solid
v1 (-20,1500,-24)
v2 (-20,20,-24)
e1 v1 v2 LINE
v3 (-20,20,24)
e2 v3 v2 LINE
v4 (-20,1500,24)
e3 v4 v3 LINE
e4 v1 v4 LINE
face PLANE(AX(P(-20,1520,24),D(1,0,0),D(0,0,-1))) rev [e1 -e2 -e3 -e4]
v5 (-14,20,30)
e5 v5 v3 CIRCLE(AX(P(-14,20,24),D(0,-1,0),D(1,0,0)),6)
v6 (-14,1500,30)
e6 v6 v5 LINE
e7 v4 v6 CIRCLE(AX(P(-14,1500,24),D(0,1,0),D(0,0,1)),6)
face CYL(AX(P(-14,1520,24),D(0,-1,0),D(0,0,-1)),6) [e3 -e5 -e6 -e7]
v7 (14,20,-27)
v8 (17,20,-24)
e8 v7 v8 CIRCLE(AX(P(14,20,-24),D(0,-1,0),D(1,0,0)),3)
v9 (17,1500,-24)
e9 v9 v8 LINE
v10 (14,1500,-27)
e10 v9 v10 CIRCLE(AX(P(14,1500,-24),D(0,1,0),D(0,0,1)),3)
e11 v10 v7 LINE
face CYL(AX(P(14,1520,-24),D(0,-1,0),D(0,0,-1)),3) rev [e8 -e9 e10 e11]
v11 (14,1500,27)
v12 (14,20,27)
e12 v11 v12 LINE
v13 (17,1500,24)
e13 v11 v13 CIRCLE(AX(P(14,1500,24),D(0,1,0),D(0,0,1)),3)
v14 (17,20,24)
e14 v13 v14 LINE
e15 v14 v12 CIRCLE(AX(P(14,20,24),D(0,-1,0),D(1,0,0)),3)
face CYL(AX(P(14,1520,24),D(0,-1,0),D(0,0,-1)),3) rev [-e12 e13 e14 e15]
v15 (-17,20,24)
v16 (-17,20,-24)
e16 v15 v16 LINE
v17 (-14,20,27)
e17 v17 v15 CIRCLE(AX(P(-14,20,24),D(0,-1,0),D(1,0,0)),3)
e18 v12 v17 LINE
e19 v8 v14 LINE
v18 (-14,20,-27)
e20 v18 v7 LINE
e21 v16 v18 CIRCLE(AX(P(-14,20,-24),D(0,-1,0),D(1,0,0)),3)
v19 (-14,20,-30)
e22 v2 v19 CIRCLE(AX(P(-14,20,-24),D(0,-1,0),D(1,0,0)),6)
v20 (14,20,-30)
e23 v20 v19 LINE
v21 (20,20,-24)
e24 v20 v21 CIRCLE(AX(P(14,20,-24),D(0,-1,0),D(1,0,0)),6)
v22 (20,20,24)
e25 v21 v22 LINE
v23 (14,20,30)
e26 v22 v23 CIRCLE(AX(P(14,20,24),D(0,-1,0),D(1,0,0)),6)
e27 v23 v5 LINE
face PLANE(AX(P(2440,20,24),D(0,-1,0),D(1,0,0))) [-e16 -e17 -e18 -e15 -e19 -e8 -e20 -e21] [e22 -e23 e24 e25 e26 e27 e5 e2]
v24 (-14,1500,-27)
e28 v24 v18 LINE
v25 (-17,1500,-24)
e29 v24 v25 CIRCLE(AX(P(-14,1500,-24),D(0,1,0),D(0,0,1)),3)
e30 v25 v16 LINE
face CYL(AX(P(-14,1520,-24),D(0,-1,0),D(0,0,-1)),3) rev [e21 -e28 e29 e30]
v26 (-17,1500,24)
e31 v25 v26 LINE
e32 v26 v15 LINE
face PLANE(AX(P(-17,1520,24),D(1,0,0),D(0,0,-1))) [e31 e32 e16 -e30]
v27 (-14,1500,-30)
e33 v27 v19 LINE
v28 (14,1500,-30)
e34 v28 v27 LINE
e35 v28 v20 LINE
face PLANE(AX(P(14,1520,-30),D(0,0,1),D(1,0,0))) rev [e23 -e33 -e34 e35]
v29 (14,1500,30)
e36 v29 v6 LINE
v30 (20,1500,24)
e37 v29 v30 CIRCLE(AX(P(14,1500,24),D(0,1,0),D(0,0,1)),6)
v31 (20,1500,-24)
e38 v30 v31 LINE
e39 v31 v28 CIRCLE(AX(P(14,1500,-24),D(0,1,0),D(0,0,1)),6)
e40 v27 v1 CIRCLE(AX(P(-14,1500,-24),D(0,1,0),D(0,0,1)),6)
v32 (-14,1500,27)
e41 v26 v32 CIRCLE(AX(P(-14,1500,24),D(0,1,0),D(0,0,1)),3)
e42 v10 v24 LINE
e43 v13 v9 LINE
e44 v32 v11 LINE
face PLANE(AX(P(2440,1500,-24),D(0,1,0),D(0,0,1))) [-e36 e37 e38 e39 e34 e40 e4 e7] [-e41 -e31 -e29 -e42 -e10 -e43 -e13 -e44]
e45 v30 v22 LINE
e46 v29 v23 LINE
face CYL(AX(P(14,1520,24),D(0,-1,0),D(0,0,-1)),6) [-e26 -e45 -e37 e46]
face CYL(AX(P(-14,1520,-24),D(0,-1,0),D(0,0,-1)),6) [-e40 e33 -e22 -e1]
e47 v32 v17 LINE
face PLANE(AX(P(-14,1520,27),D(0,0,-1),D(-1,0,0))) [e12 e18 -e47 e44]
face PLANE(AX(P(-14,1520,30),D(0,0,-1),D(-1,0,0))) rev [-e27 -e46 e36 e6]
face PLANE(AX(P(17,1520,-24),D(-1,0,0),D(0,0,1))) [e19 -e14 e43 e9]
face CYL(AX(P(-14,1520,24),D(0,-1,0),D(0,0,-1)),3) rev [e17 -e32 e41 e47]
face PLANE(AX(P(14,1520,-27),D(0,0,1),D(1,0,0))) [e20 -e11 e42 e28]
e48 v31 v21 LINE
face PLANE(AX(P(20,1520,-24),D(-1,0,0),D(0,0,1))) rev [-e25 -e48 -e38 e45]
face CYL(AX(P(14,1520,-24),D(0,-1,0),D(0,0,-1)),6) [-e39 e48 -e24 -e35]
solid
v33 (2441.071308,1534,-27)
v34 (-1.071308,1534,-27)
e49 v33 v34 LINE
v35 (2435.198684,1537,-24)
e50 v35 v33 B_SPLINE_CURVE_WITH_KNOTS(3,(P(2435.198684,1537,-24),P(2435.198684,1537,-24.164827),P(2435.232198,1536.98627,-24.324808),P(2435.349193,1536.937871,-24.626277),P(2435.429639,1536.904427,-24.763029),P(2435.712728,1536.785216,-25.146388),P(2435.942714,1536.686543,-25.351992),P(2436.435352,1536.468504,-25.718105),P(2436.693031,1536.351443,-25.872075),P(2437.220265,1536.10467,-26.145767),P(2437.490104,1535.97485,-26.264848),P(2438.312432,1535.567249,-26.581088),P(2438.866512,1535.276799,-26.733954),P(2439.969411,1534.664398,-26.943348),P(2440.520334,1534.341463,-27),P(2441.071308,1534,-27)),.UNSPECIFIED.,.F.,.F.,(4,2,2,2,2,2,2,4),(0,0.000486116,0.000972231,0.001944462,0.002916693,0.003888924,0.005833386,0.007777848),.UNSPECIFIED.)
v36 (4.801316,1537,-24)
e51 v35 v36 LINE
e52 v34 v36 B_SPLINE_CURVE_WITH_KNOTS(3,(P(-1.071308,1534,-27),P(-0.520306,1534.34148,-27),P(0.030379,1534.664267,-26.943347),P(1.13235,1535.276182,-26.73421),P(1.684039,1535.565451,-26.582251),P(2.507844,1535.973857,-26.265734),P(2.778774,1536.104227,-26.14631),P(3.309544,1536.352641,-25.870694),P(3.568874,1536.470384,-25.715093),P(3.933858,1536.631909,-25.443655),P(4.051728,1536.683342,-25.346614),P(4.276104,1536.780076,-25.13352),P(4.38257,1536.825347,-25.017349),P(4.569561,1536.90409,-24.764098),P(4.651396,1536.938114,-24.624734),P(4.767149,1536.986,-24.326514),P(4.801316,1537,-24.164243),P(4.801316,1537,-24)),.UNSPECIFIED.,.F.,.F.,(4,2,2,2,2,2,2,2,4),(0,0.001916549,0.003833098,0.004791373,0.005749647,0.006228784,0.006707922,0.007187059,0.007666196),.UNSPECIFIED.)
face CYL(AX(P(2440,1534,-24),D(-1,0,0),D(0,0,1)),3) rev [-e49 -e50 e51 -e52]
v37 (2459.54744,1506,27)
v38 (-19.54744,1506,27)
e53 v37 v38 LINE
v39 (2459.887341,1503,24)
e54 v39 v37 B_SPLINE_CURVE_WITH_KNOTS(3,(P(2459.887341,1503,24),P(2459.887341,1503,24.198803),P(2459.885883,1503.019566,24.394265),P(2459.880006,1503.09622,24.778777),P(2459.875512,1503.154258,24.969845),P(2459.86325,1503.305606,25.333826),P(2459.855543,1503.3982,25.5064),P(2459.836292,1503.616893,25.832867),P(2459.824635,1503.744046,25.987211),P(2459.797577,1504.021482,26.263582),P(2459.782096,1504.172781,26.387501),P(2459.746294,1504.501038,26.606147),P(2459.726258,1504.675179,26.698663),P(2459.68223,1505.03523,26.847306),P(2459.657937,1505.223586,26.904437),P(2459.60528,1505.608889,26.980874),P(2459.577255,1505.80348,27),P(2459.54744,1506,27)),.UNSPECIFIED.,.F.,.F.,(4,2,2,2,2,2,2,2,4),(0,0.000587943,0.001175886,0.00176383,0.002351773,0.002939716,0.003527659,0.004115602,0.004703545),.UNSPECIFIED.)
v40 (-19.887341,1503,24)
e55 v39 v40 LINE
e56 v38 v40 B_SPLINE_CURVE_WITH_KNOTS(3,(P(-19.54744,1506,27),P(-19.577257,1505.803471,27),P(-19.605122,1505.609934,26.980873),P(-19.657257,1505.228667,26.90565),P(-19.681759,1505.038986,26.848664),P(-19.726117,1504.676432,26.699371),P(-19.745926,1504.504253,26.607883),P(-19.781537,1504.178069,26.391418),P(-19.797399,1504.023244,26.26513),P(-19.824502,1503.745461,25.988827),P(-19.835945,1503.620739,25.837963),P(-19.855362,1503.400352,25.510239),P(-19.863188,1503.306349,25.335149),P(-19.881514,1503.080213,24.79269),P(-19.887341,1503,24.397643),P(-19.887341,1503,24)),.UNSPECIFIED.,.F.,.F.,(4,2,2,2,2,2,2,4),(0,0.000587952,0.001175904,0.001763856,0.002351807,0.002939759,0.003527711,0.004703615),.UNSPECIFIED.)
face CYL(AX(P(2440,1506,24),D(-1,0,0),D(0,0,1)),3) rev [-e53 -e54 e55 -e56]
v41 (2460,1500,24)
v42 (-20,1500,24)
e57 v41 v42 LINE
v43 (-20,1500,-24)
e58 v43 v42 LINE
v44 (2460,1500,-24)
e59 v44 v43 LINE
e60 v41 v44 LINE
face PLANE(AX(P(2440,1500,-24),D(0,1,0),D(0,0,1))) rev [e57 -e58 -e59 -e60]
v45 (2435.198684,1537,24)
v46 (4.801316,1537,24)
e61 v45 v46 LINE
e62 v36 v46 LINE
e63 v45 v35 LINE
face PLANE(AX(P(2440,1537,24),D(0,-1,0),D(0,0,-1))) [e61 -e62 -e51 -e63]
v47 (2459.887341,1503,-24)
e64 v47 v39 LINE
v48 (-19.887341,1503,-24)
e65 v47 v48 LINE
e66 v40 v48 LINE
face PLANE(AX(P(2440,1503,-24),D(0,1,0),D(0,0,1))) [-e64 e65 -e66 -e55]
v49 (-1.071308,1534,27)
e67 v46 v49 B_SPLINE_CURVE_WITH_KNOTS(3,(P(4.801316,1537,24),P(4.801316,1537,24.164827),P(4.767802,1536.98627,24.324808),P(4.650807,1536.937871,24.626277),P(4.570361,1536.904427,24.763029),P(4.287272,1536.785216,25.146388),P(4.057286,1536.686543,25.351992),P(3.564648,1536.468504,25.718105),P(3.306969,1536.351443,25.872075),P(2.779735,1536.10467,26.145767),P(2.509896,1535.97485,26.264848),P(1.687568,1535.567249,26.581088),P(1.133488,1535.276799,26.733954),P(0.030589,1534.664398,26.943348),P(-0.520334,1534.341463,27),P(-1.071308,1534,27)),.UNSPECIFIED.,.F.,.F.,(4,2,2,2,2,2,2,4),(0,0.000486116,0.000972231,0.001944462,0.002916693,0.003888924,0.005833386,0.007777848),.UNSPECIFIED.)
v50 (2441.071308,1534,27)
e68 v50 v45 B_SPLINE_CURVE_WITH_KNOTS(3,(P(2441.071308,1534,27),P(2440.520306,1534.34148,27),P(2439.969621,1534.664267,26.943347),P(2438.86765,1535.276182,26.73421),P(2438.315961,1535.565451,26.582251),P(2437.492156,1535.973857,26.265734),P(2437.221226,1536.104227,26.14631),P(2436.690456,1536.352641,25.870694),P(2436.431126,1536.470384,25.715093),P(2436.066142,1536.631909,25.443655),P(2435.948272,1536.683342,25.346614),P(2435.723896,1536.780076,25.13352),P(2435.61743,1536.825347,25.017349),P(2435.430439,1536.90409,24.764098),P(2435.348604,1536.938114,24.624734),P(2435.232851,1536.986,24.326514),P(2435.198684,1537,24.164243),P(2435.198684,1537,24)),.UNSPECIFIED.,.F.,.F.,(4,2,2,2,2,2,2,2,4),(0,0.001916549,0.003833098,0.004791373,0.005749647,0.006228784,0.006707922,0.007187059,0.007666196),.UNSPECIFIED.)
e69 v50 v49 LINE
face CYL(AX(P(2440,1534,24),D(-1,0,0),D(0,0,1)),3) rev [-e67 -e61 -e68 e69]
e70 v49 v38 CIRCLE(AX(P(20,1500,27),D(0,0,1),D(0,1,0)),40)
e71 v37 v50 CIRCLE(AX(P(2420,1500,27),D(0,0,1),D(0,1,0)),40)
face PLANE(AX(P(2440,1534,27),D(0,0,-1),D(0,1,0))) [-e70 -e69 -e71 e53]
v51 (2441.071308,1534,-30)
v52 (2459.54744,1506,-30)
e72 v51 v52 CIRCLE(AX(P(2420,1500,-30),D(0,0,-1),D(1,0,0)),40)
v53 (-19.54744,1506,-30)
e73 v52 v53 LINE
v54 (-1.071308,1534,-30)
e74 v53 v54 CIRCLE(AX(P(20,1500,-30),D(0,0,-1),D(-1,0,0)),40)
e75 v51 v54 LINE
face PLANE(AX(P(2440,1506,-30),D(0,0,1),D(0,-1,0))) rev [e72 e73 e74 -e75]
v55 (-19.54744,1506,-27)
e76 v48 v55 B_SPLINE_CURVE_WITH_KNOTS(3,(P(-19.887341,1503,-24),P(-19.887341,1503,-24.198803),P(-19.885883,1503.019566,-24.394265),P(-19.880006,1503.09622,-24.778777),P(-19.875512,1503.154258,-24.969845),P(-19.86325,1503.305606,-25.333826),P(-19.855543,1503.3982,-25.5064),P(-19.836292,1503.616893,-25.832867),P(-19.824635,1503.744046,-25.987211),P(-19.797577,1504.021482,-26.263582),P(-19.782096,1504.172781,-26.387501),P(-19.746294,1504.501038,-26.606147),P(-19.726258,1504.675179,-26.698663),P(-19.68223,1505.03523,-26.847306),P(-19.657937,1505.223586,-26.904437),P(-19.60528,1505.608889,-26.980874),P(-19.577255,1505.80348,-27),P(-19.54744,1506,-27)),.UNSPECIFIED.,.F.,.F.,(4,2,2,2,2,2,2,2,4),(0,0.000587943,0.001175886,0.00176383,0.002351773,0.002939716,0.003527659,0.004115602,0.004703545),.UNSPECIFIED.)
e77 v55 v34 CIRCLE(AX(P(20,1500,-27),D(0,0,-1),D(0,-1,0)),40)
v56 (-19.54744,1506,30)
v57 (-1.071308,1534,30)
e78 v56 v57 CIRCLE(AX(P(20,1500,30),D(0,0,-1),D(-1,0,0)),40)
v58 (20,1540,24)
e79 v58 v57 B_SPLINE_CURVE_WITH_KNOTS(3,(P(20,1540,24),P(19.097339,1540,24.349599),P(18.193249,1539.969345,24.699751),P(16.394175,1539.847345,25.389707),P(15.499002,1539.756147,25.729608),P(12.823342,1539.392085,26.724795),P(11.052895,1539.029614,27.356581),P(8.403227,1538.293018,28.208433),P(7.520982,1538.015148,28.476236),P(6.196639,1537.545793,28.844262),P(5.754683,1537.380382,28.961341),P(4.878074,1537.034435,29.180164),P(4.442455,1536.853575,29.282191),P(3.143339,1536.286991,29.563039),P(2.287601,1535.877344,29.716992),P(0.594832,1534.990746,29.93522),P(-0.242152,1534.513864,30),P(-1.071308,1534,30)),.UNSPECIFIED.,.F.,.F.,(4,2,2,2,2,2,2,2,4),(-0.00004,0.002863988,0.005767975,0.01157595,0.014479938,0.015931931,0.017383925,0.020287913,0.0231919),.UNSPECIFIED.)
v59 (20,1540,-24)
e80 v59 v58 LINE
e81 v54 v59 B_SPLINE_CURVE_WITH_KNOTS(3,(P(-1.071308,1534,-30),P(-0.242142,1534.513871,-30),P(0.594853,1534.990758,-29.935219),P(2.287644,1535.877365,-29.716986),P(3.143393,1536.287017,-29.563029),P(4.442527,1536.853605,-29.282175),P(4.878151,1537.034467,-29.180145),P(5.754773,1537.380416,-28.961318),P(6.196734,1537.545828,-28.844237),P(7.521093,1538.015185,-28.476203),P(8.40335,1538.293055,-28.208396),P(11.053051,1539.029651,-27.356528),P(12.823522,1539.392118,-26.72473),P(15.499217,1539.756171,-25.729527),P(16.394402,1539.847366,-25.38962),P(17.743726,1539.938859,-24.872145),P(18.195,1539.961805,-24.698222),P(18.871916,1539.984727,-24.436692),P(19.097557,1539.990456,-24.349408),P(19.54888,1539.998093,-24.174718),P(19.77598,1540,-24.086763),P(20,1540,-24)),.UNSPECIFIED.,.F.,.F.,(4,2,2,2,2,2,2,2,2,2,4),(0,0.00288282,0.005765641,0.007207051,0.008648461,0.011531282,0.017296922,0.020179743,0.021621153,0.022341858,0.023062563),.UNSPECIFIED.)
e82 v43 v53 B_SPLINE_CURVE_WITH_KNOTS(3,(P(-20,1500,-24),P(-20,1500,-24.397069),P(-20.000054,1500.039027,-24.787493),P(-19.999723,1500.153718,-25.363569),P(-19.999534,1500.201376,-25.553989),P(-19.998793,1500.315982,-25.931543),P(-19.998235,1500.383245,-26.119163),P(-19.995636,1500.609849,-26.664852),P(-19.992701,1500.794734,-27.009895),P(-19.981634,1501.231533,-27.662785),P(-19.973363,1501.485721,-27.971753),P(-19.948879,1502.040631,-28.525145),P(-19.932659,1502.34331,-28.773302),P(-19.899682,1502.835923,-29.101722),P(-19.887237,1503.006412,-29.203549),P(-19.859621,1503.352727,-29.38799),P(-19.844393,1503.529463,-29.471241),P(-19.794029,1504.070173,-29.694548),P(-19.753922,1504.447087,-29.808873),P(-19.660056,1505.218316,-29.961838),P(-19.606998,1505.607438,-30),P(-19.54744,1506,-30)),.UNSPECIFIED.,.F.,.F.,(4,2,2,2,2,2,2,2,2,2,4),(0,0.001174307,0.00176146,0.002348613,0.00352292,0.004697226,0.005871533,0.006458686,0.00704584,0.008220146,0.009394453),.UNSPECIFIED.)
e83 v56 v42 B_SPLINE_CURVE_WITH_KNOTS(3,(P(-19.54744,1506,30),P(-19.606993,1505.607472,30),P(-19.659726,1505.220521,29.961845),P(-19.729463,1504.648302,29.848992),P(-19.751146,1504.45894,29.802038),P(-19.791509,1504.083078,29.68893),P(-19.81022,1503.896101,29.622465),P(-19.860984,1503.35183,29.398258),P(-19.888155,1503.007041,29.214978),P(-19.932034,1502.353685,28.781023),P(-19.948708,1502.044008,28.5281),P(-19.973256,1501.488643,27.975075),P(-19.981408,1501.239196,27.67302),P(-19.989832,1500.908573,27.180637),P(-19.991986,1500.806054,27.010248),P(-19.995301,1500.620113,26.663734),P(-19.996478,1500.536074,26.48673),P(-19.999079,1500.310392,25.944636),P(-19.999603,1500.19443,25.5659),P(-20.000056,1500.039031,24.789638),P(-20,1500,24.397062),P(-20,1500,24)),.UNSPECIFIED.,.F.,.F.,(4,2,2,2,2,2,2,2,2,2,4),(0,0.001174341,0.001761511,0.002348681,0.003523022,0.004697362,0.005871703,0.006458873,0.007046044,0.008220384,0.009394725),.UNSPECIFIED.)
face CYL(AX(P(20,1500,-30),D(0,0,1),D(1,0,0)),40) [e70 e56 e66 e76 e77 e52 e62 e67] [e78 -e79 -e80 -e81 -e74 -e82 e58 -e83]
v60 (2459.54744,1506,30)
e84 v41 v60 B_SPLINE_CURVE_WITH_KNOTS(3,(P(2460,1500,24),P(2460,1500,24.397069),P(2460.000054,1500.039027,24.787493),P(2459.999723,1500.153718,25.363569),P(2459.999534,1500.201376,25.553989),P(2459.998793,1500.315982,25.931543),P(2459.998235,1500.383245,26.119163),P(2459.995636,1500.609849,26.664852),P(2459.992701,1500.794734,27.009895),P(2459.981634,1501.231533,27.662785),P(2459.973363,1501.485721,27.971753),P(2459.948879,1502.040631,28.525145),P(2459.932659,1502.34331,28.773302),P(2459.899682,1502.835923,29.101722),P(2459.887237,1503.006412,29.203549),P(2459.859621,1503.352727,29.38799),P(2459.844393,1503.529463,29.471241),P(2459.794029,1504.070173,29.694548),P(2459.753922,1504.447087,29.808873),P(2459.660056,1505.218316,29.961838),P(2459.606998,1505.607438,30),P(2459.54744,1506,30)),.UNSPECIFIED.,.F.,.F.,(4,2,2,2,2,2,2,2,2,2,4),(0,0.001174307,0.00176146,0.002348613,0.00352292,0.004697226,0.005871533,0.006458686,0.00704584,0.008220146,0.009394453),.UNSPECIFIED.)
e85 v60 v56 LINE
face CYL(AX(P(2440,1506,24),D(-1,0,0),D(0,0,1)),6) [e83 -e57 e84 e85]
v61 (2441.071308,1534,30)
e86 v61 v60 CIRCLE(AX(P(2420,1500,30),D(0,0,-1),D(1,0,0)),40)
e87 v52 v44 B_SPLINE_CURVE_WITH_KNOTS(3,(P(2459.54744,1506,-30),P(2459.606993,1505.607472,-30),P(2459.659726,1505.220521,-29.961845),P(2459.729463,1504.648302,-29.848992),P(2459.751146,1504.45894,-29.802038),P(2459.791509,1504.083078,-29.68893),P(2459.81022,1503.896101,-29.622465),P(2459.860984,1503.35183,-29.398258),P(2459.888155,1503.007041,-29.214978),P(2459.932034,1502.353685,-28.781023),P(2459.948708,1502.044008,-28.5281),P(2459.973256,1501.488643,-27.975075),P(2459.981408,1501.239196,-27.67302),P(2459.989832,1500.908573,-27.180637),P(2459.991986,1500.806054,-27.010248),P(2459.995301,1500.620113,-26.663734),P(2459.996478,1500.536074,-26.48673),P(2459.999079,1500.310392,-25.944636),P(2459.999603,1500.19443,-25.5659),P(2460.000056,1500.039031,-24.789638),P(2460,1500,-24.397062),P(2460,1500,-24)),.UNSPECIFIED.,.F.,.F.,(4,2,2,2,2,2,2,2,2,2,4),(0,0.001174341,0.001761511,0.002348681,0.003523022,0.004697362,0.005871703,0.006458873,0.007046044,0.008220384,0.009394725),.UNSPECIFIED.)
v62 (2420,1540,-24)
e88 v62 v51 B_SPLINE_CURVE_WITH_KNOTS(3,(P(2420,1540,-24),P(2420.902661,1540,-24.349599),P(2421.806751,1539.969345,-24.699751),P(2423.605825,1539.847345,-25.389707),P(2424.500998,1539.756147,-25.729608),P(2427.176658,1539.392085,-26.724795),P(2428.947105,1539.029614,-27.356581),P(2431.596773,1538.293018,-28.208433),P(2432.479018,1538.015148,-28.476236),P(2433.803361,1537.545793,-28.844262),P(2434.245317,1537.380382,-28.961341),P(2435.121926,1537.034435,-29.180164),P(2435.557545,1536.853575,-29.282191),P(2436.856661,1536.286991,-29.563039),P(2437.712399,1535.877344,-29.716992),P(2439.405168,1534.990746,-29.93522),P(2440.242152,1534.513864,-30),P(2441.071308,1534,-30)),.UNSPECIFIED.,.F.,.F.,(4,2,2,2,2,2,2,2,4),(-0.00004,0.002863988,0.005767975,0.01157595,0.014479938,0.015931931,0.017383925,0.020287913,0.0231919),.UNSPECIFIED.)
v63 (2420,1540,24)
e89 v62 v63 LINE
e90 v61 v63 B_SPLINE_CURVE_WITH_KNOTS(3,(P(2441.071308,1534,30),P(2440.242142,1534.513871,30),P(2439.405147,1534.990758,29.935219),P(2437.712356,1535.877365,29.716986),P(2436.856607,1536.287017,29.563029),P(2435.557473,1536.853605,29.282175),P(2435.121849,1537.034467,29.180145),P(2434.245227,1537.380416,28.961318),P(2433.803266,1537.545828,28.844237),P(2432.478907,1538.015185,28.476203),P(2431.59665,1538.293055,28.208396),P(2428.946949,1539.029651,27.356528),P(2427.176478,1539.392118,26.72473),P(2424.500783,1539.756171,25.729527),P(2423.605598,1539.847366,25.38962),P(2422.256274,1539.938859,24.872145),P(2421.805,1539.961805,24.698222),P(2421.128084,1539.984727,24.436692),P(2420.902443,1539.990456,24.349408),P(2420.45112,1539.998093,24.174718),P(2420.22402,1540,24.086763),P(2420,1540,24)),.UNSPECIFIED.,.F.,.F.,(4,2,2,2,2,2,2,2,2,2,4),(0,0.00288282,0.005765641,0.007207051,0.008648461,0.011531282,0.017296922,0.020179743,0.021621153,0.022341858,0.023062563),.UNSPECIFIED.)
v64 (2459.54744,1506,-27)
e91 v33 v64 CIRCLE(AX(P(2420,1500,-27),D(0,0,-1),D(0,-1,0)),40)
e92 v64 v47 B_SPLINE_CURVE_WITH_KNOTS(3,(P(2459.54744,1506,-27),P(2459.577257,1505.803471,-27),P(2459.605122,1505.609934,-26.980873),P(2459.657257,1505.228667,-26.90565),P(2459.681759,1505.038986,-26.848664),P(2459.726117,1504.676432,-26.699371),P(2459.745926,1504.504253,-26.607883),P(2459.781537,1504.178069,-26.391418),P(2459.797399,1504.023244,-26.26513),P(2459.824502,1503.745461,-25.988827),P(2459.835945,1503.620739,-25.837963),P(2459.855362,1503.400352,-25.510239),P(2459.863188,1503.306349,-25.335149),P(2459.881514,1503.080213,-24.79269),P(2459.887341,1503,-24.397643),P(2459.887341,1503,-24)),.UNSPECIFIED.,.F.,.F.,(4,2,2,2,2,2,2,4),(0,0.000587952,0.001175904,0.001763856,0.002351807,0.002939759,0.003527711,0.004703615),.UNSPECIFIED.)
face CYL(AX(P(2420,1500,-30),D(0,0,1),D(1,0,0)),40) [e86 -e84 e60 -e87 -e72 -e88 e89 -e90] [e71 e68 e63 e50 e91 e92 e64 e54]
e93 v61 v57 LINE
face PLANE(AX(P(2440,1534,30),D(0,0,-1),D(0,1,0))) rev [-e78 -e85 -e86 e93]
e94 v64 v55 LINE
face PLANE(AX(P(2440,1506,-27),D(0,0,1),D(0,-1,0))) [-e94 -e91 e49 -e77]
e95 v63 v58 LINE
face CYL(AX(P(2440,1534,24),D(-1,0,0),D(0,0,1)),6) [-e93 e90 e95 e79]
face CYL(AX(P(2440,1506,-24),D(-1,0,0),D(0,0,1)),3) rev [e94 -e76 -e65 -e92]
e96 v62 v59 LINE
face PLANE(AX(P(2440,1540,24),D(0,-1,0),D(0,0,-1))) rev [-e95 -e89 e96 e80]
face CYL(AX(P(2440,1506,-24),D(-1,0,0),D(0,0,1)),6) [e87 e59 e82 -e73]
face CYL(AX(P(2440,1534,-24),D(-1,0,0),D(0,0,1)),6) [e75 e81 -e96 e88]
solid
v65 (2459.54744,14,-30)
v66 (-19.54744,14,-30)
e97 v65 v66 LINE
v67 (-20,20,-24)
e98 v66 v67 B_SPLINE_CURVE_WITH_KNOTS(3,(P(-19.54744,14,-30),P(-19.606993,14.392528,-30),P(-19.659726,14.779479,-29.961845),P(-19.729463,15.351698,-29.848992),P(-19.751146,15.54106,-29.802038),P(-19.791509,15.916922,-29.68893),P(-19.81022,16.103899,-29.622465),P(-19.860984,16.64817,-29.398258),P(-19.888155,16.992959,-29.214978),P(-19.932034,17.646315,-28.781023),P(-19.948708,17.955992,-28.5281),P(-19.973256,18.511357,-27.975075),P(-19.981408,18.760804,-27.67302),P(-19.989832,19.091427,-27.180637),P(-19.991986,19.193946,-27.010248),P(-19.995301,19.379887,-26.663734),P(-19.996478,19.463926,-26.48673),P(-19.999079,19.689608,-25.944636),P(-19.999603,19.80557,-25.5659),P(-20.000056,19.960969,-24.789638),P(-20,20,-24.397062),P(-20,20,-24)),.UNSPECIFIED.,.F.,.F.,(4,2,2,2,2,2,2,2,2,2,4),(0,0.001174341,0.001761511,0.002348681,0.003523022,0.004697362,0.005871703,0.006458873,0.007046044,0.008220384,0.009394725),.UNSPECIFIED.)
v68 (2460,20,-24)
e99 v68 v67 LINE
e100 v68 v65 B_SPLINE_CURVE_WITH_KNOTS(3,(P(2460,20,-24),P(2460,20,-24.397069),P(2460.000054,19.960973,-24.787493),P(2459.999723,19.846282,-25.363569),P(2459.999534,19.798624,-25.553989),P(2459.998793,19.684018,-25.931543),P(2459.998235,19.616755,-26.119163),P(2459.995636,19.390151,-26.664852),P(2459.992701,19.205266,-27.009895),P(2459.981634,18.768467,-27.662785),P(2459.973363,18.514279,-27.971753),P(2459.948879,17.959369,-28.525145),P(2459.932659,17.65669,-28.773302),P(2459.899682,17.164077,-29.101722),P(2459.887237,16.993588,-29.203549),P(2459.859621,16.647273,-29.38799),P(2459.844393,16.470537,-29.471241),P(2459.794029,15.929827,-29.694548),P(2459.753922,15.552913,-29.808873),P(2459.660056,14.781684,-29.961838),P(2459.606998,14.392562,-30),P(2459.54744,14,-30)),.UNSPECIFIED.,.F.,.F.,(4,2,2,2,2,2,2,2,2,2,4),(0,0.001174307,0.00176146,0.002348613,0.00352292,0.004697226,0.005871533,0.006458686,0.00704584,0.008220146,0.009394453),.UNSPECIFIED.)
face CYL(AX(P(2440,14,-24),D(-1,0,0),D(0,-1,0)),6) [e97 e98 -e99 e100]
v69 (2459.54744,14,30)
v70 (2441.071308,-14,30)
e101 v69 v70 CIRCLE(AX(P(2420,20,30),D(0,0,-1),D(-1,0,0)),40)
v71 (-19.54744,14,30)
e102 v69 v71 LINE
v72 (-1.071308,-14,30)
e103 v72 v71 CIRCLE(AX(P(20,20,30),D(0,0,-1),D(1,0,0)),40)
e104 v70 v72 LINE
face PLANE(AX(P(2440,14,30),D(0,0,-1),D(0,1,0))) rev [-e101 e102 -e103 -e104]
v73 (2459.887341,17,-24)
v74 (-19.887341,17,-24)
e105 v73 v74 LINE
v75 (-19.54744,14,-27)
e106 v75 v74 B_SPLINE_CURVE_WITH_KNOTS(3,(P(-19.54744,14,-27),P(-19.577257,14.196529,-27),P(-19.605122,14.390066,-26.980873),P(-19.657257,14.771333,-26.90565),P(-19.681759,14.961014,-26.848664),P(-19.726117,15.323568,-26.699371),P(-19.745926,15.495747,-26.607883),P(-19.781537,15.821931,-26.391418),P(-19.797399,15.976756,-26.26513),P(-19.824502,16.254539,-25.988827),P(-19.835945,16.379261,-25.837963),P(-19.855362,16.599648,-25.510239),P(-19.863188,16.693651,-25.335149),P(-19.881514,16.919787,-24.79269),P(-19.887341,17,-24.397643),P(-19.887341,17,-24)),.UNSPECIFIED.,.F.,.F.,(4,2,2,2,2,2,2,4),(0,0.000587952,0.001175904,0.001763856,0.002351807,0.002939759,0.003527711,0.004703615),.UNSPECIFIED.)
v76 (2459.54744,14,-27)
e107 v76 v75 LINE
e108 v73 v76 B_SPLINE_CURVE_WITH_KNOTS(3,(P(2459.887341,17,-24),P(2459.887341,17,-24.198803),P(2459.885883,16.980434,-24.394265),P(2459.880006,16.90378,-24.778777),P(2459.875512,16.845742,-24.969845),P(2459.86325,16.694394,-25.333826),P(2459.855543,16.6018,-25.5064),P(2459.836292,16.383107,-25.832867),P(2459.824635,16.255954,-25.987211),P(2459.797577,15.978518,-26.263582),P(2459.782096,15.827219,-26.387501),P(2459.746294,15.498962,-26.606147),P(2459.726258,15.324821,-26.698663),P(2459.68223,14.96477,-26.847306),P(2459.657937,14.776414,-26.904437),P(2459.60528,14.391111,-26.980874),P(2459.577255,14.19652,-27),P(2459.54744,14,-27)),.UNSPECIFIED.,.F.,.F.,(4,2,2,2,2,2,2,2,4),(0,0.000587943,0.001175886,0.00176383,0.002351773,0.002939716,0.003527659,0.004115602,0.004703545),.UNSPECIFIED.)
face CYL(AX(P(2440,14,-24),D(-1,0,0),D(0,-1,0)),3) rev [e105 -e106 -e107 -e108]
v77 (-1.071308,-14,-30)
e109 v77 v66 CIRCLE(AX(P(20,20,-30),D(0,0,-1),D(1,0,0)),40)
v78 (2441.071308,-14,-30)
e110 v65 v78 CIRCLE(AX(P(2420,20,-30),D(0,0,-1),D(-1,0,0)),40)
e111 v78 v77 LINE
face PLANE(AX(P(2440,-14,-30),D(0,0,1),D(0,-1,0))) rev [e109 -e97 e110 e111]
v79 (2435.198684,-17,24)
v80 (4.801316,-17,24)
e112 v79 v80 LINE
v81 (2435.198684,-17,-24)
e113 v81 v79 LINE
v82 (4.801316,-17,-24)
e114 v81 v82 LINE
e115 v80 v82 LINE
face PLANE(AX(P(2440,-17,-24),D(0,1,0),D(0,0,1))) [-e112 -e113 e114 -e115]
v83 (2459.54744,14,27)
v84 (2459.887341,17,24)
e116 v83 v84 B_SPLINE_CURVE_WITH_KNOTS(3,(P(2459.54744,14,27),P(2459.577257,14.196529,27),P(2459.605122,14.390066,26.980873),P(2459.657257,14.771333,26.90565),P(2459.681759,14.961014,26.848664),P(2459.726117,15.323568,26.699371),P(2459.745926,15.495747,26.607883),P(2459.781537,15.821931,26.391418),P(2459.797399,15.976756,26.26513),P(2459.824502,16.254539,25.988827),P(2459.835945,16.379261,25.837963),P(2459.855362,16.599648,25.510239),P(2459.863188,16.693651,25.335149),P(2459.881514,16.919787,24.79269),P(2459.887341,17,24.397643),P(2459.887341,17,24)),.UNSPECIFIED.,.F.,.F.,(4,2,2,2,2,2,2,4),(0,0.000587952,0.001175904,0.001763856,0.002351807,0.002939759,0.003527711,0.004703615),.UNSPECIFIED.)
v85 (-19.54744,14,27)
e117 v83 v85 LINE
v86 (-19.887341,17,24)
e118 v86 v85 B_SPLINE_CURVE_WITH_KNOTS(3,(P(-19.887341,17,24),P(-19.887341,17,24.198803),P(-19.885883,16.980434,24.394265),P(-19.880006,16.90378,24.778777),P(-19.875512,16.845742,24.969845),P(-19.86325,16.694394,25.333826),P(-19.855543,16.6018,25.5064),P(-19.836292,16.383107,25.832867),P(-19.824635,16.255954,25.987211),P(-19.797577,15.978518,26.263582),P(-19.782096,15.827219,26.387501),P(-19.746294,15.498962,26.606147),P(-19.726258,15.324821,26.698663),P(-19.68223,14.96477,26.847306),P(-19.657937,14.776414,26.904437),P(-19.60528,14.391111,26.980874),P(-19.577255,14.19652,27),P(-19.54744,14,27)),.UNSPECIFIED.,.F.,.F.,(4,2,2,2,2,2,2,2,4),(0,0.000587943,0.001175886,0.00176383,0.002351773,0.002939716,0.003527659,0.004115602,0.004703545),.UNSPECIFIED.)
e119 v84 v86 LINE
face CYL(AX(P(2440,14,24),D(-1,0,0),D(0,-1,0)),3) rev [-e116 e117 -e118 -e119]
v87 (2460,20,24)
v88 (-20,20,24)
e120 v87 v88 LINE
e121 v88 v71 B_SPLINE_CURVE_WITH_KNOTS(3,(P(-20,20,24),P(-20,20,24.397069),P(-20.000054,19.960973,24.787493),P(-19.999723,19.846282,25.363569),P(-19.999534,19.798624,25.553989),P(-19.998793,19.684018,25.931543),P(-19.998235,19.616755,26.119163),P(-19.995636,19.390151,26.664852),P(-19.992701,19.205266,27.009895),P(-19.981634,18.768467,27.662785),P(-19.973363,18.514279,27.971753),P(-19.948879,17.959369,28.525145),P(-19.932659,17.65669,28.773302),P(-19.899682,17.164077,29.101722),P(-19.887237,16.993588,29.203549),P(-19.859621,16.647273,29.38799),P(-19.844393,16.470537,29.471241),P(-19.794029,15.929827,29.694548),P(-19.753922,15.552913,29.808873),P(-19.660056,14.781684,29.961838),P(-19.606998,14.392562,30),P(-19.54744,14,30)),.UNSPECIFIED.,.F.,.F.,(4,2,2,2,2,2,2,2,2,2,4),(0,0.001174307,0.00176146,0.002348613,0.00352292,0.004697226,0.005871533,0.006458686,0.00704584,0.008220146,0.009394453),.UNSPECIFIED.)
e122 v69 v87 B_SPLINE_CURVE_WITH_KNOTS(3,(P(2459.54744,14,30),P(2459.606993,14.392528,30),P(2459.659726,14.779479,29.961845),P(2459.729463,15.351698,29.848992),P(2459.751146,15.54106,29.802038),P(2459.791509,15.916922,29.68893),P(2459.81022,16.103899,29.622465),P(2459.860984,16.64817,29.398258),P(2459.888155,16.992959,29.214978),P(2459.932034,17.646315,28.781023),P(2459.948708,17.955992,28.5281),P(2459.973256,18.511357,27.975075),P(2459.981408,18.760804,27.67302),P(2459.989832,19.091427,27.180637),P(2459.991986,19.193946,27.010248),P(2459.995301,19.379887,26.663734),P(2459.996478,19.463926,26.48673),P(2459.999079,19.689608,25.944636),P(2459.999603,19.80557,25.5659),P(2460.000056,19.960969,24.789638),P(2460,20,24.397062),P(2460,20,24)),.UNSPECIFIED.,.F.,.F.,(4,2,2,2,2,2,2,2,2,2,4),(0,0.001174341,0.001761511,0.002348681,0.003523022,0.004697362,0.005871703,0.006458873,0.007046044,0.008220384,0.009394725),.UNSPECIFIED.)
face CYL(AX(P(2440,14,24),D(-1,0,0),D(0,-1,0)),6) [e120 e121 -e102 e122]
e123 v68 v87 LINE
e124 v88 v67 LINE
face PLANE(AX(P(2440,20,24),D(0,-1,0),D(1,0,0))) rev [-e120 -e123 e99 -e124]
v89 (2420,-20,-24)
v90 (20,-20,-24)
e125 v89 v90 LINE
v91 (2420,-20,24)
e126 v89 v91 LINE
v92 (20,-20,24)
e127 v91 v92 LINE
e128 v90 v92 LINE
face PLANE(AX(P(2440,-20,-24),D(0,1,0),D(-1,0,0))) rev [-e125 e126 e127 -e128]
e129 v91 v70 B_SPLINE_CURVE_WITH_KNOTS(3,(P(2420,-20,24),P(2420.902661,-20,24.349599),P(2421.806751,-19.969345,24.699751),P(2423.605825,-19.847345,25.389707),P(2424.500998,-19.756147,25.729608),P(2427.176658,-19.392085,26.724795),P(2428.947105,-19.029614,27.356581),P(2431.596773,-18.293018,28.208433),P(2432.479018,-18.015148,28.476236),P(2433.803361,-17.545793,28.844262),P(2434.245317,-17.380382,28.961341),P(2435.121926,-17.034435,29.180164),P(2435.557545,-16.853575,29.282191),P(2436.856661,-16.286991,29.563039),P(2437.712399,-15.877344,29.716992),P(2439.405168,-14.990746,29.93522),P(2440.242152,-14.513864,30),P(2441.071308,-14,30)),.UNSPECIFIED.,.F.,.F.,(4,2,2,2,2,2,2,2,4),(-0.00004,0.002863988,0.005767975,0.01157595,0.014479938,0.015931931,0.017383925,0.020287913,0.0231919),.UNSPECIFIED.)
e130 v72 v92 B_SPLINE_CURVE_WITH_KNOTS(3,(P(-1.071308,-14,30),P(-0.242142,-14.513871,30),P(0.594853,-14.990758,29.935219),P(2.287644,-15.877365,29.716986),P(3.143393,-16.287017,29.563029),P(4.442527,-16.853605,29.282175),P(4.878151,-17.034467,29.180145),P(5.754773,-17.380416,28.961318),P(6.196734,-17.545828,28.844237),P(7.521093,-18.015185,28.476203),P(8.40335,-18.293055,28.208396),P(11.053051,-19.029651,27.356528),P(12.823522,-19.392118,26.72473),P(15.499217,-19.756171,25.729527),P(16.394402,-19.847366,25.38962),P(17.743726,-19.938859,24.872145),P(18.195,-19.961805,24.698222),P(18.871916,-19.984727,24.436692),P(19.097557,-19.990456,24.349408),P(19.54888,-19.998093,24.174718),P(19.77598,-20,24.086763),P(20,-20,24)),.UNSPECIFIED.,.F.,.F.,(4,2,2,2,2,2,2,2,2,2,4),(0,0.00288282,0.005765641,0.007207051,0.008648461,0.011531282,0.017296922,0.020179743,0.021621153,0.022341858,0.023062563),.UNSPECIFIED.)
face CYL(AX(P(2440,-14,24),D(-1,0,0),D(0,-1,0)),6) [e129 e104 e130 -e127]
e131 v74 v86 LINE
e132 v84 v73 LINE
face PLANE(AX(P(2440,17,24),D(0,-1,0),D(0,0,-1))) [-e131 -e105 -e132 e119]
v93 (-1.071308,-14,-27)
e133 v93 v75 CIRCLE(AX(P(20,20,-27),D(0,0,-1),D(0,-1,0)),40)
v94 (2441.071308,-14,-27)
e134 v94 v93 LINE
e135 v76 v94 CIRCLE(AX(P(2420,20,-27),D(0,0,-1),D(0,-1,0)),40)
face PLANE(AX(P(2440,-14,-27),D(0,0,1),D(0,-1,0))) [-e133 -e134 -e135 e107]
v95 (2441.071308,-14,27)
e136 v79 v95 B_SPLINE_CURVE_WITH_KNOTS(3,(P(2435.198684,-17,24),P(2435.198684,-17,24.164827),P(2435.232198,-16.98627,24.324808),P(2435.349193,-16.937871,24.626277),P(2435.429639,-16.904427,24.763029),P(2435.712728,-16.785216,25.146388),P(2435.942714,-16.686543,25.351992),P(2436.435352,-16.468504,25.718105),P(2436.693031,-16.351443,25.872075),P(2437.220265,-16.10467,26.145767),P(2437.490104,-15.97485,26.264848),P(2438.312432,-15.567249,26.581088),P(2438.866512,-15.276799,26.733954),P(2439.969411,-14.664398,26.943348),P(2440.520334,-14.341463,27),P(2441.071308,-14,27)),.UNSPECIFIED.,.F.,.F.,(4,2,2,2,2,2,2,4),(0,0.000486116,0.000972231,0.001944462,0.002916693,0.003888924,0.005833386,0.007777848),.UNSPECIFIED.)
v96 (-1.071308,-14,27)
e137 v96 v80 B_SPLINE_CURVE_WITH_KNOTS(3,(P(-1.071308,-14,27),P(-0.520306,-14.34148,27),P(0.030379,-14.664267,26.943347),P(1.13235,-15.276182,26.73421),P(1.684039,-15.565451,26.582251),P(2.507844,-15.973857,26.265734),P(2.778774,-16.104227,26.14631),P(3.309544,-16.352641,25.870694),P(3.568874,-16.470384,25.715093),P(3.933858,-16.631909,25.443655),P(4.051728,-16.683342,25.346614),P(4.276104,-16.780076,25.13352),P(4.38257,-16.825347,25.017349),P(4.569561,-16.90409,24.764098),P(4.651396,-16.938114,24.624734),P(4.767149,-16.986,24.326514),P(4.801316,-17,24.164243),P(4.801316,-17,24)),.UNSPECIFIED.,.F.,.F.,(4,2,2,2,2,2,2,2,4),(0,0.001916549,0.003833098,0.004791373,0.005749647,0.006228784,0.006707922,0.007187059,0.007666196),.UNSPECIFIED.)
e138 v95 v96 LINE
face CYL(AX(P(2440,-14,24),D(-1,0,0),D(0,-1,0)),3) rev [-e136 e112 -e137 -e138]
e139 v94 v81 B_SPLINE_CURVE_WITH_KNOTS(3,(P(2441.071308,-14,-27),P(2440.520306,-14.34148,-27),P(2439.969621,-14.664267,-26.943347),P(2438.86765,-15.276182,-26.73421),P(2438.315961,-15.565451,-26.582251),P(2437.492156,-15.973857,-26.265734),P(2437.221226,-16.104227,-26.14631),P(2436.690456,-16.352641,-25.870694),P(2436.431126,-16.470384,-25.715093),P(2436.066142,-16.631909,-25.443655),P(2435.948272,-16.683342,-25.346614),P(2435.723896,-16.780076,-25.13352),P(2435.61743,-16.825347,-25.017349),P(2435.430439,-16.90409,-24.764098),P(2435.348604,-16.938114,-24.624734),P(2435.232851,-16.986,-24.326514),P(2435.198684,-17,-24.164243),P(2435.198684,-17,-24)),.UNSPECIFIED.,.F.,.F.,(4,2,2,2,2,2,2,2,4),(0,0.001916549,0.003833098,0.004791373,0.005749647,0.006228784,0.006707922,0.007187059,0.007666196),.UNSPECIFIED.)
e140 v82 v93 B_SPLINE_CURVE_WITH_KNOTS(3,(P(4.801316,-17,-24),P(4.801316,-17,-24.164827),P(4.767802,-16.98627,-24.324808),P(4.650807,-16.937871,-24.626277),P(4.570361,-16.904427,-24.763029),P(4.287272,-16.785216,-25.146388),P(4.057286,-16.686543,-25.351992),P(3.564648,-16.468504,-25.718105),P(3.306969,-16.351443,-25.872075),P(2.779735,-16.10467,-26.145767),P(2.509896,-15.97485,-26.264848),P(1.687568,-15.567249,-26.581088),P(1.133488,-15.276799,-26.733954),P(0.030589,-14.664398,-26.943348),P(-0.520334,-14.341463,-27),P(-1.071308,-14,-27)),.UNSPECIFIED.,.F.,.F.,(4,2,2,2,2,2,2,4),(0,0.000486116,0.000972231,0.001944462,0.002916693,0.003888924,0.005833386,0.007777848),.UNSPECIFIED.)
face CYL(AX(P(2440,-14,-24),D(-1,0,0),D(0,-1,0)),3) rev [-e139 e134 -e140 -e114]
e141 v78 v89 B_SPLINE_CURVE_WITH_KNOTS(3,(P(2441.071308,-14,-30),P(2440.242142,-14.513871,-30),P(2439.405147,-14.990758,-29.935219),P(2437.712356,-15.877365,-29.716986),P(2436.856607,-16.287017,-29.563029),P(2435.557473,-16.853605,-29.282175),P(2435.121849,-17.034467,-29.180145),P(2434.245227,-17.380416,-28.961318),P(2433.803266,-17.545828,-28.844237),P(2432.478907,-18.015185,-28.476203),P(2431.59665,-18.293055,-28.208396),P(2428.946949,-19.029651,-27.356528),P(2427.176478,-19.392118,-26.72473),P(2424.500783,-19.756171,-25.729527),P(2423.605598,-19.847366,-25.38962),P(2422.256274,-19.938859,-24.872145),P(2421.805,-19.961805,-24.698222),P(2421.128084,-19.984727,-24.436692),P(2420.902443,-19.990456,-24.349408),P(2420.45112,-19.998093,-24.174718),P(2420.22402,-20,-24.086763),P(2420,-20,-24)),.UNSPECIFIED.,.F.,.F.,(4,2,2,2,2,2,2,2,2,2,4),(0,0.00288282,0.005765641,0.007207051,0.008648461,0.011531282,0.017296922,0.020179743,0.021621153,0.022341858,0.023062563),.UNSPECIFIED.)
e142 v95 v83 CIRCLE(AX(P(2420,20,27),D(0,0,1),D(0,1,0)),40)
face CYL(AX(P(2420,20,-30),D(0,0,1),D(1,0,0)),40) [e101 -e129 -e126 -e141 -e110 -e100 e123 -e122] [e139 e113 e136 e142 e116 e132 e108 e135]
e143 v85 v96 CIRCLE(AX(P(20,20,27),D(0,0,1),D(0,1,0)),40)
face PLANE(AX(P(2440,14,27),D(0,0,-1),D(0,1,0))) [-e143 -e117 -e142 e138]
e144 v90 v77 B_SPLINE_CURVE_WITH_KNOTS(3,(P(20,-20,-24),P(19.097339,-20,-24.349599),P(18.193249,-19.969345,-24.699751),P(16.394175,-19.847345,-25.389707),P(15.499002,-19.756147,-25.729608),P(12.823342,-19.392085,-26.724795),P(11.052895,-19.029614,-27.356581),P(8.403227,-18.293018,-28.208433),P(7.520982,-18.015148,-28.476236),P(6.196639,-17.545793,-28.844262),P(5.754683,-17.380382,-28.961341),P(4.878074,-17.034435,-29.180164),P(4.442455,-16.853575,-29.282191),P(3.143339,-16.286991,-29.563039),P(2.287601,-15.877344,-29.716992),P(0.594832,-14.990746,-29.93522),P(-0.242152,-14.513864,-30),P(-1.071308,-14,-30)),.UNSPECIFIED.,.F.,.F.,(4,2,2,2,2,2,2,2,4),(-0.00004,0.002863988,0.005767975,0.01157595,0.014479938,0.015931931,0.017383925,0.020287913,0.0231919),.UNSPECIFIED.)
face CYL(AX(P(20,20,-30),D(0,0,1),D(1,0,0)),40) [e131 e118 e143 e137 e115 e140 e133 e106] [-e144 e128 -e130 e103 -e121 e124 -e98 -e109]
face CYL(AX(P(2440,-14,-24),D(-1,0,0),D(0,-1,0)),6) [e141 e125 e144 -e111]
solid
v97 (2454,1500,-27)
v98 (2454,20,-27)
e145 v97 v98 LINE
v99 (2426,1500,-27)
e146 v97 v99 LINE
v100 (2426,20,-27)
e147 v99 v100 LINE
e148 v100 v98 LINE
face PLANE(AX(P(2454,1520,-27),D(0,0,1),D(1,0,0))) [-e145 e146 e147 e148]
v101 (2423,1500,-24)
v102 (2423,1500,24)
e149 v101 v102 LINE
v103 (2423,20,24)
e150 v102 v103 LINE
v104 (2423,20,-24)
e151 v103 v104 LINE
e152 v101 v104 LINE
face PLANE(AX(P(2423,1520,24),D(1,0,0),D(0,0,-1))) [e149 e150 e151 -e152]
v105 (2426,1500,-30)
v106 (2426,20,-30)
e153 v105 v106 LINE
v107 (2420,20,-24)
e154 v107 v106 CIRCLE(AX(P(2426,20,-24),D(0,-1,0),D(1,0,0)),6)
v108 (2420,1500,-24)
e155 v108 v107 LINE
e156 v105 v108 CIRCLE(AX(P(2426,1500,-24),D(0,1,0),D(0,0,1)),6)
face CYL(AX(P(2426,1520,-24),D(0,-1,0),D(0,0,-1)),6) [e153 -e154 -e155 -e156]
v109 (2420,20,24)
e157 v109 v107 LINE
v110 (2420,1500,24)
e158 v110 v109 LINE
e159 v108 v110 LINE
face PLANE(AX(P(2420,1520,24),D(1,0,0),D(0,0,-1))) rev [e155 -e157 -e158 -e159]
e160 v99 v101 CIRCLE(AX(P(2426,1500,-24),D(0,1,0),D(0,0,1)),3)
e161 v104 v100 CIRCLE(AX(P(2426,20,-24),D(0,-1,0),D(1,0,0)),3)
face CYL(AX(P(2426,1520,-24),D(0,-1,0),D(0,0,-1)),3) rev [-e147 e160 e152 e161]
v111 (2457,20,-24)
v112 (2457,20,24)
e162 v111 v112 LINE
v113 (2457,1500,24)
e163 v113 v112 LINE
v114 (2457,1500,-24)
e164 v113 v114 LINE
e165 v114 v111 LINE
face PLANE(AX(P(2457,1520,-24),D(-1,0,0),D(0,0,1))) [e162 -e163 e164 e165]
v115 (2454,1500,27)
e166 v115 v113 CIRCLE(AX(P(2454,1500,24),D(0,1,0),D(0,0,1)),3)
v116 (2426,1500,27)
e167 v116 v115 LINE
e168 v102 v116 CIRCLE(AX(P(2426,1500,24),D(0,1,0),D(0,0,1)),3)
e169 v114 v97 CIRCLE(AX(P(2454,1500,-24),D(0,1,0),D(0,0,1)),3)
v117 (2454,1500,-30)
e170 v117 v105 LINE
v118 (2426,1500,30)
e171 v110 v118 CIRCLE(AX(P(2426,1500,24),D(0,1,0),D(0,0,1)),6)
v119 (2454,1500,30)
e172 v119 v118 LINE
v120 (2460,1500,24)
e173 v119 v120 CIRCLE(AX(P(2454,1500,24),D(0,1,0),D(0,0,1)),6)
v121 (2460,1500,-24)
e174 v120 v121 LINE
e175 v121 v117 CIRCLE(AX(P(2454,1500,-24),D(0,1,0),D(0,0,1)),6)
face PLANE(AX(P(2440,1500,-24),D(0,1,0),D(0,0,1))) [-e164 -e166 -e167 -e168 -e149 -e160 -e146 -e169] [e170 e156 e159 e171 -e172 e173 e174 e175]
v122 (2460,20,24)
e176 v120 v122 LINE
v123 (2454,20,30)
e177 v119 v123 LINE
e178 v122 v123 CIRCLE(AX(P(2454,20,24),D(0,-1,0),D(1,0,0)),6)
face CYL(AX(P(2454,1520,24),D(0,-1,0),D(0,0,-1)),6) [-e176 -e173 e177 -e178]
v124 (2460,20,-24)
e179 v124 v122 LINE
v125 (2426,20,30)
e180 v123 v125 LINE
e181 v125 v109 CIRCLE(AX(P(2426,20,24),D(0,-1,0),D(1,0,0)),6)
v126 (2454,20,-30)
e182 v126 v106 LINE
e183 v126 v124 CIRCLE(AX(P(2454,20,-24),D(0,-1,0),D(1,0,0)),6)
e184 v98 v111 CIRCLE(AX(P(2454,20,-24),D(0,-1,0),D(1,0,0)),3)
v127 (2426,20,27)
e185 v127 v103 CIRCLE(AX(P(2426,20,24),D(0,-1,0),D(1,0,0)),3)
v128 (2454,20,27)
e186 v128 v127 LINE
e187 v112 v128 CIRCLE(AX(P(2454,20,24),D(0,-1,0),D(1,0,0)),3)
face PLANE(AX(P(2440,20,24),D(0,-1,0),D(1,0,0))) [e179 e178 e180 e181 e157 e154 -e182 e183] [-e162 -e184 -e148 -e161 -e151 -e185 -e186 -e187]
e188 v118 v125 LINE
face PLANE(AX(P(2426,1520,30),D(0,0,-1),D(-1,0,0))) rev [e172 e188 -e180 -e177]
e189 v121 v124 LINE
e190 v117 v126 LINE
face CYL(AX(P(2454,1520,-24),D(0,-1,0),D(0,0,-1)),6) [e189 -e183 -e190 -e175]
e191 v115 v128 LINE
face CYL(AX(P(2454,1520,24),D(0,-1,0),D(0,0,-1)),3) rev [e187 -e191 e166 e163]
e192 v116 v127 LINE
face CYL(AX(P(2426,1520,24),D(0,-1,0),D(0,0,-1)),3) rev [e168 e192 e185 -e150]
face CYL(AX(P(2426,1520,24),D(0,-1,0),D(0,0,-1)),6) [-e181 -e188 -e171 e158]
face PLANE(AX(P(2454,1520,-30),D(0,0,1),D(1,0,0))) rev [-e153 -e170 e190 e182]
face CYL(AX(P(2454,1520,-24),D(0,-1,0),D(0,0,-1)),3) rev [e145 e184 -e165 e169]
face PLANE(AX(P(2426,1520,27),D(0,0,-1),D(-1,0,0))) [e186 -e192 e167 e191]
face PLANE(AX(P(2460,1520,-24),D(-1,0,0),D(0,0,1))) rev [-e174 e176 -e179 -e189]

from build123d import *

# Parameters (mm, degrees)
GB_6728_1986_RECT_HOLLOW_SECTION_060_X_4_DEPTH      = 2460
GB_6728_1986_RECT_HOLLOW_SECTION_060_X_4_DEPTH_BACK = 20
GB_6728_1986_RECT_HOLLOW_SECTION_060_2_DEPTH        = 2480
GB_6728_1986_RECT_HOLLOW_SECTION_060_3_DEPTH        = 1522
GB_6728_1986_RECT_HOLLOW_SECTION_060_5_DEPTH        = 1522
CUT_EXTRUDE1_DEPTH                                  = 2877.6821166058676


with BuildPart() as part:
    # Sketch14 → GB/6728-1986 rect hollow section 060 X 40 X 3(1) (new, two sides: drawn at the far end of the back side and taken through both)
    with BuildSketch(Plane(origin=(0, 1520, 0), x_dir=(0, 1, 3.49e-15), z_dir=(1, 0, 0)).offset(-GB_6728_1986_RECT_HOLLOW_SECTION_060_X_4_DEPTH_BACK)):
        with BuildLine():
            Line((-14, -30), (14, -30))
            ThreePointArc((14, -30), (18.242640687119284, -28.242640687119284), (20.000000000000004, -24))
            Line((20.000000000000004, -24), (20.000000000000004, 24))
            ThreePointArc((20.000000000000004, 24), (18.242640687119287, 28.242640687119287), (14, 30))
            Line((14, 30), (-14, 30))
            ThreePointArc((-14, 30), (-18.242640687119284, 28.242640687119284), (-20.000000000000004, 24))
            Line((-20.000000000000004, 24), (-20.000000000000004, -24))
            ThreePointArc((-20.000000000000004, -24), (-18.242640687119287, -28.242640687119287), (-14, -30))
        make_face()
        with BuildLine():
            Line((-14, -27.000000000000004), (14, -27.000000000000004))
            ThreePointArc((14, -27.000000000000004), (16.121320343559645, -26.121320343559645), (17, -24))
            Line((17, -24), (17, 24))
            ThreePointArc((17, 24), (16.121320343559642, 26.121320343559642), (14, 27.000000000000004))
            Line((14, 27.000000000000004), (-14, 27.000000000000004))
            ThreePointArc((-14, 27.000000000000004), (-16.121320343559645, 26.121320343559645), (-17, 24))
            Line((-17, 24), (-17, -24))
            ThreePointArc((-17, -24), (-16.121320343559642, -26.121320343559642), (-14, -27.000000000000004))
        make_face(mode=Mode.SUBTRACT)
    extrude(amount=GB_6728_1986_RECT_HOLLOW_SECTION_060_X_4_DEPTH + GB_6728_1986_RECT_HOLLOW_SECTION_060_X_4_DEPTH_BACK)


with BuildPart() as body_2:
    # Sketch14 on segment 2 (carried to segment 2) → GB_6728-1986 rect hollow section 060 2 (new body)
    with BuildSketch(Plane.YZ.offset(-20)):
        with BuildLine():
            Line((-14, -30), (14, -30))
            ThreePointArc((14, -30), (18.242640687119284, -28.242640687119284), (20.000000000000004, -24))
            Line((20.000000000000004, -24), (20.000000000000004, 24))
            ThreePointArc((20.000000000000004, 24), (18.242640687119287, 28.242640687119287), (14, 30))
            Line((14, 30), (-14, 30))
            ThreePointArc((-14, 30), (-18.242640687119284, 28.242640687119284), (-20.000000000000004, 24))
            Line((-20.000000000000004, 24), (-20.000000000000004, -24))
            ThreePointArc((-20.000000000000004, -24), (-18.242640687119287, -28.242640687119287), (-14, -30))
        make_face()
        with BuildLine():
            Line((-14, -27.000000000000004), (14, -27.000000000000004))
            ThreePointArc((14, -27.000000000000004), (16.121320343559645, -26.121320343559645), (17, -24))
            Line((17, -24), (17, 24))
            ThreePointArc((17, 24), (16.121320343559642, 26.121320343559642), (14, 27.000000000000004))
            Line((14, 27.000000000000004), (-14, 27.000000000000004))
            ThreePointArc((-14, 27.000000000000004), (-16.121320343559645, 26.121320343559645), (-17, 24))
            Line((-17, 24), (-17, -24))
            ThreePointArc((-17, -24), (-16.121320343559642, -26.121320343559642), (-14, -27.000000000000004))
        make_face(mode=Mode.SUBTRACT)
    extrude(amount=GB_6728_1986_RECT_HOLLOW_SECTION_060_2_DEPTH)


with BuildPart() as body_3:
    # Sketch14 on segment 3 (carried to segment 3) → GB_6728-1986 rect hollow section 060 3 (new body)
    with BuildSketch(Plane(origin=(0, -1, 0), x_dir=(-1, 0, 0), z_dir=(0, 1, 0))):
        with BuildLine():
            Line((-14, -30), (14, -30))
            ThreePointArc((14, -30), (18.242640687119284, -28.242640687119284), (20.000000000000004, -24))
            Line((20.000000000000004, -24), (20.000000000000004, 24))
            ThreePointArc((20.000000000000004, 24), (18.242640687119287, 28.242640687119287), (14, 30))
            Line((14, 30), (-14, 30))
            ThreePointArc((-14, 30), (-18.242640687119284, 28.242640687119284), (-20.000000000000004, 24))
            Line((-20.000000000000004, 24), (-20.000000000000004, -24))
            ThreePointArc((-20.000000000000004, -24), (-18.242640687119287, -28.242640687119287), (-14, -30))
        make_face()
        with BuildLine():
            Line((-14, -27.000000000000004), (14, -27.000000000000004))
            ThreePointArc((14, -27.000000000000004), (16.121320343559645, -26.121320343559645), (17, -24))
            Line((17, -24), (17, 24))
            ThreePointArc((17, 24), (16.121320343559642, 26.121320343559642), (14, 27.000000000000004))
            Line((14, 27.000000000000004), (-14, 27.000000000000004))
            ThreePointArc((-14, 27.000000000000004), (-16.121320343559645, 26.121320343559645), (-17, 24))
            Line((-17, 24), (-17, -24))
            ThreePointArc((-17, -24), (-16.121320343559642, -26.121320343559642), (-14, -27.000000000000004))
        make_face(mode=Mode.SUBTRACT)
    extrude(amount=GB_6728_1986_RECT_HOLLOW_SECTION_060_3_DEPTH)

    # GB_6728-1986 rect hollow section 060 3 e
    split(bisect_by=Plane(origin=(0, 20, 0), x_dir=(-1, 0, 0), z_dir=(0, 1, 0)), keep=Keep.TOP)

    # GB_6728-1986 rect hollow section 060 4
    split(bisect_by=Plane.XZ.offset(-1500), keep=Keep.TOP)


with BuildPart() as body_4:
    # Sketch14 on segment 4 (carried to segment 4) → GB_6728-1986 rect hollow section 060 5 (new body)
    with BuildSketch(Plane(origin=(2440, -1, 0), x_dir=(-1, 0, 0), z_dir=(0, 1, 0))):
        with BuildLine():
            Line((-14, -30), (14, -30))
            ThreePointArc((14, -30), (18.242640687119284, -28.242640687119284), (20.000000000000004, -24))
            Line((20.000000000000004, -24), (20.000000000000004, 24))
            ThreePointArc((20.000000000000004, 24), (18.242640687119287, 28.242640687119287), (14, 30))
            Line((14, 30), (-14, 30))
            ThreePointArc((-14, 30), (-18.242640687119284, 28.242640687119284), (-20.000000000000004, 24))
            Line((-20.000000000000004, 24), (-20.000000000000004, -24))
            ThreePointArc((-20.000000000000004, -24), (-18.242640687119287, -28.242640687119287), (-14, -30))
        make_face()
        with BuildLine():
            Line((-14, -27.000000000000004), (14, -27.000000000000004))
            ThreePointArc((14, -27.000000000000004), (16.121320343559645, -26.121320343559645), (17, -24))
            Line((17, -24), (17, 24))
            ThreePointArc((17, 24), (16.121320343559642, 26.121320343559642), (14, 27.000000000000004))
            Line((14, 27.000000000000004), (-14, 27.000000000000004))
            ThreePointArc((-14, 27.000000000000004), (-16.121320343559645, 26.121320343559645), (-17, 24))
            Line((-17, 24), (-17, -24))
            ThreePointArc((-17, -24), (-16.121320343559642, -26.121320343559642), (-14, -27.000000000000004))
        make_face(mode=Mode.SUBTRACT)
    extrude(amount=GB_6728_1986_RECT_HOLLOW_SECTION_060_5_DEPTH)

    # GB_6728-1986 rect hollow section 060 5 e
    split(bisect_by=Plane(origin=(2440, 20, 0), x_dir=(-1, 0, 0), z_dir=(0, 1, 0)), keep=Keep.TOP)

    # GB_6728-1986 rect hollow section 060 6
    split(bisect_by=Plane(origin=(2440, 1500, 0), x_dir=(1, 0, 0), z_dir=(0, -1, 0)), keep=Keep.TOP)


with BuildPart() as cut_extrude1_tool:
    # Sketch2 → Cut-Extrude1 (new, through all)
    with BuildSketch(Plane(origin=(0, 1470.0000000000052, 29.999999999994724), x_dir=(1, 0, 0), z_dir=(0, 0, 1))):
        with BuildLine():
            Line((-20.000000000000014, -1450.0000000000052), (-20.000000000000018, -1490.0000000000052))
            Line((-20.000000000000018, -1490.0000000000052), (20.000000000000018, -1490.0000000000052))
            ThreePointArc((20.000000000000018, -1490.0000000000052), (-8.284271247461913, -1478.2842712474671), (-20.000000000000014, -1450.0000000000052))
        make_face()
        with BuildLine():
            Line((-20.000000000000018, 69.99999999999473), (20.000000000000018, 69.99999999999473))
            ThreePointArc((20.000000000000018, 69.99999999999473), (-8.284271247461902, 58.284271247456616), (-20.000000000000014, 29.9999999999947))
            Line((-20.000000000000014, 29.9999999999947), (-20.000000000000018, 69.99999999999473))
        make_face()
        with BuildLine():
            Line((2460, -1490.0000000000052), (2420, -1490.0000000000052))
            ThreePointArc((2420, -1490.0000000000052), (2448.284271247462, -1478.2842712474671), (2460, -1450.0000000000052))
            Line((2460, -1450.0000000000052), (2460, -1490.0000000000052))
        make_face()
        with BuildLine():
            Line((2460, 29.9999999999947), (2460, 69.99999999999473))
            Line((2460, 69.99999999999473), (2420, 69.99999999999473))
            ThreePointArc((2420, 69.99999999999473), (2448.284271247462, 58.2842712474566), (2460, 29.9999999999947))
        make_face()
    extrude(amount=-CUT_EXTRUDE1_DEPTH)


with BuildPart() as part_1:
    add(part.part)

    # Cut-Extrude1: cut by cut_extrude1_tool
    add(cut_extrude1_tool.part, mode=Mode.SUBTRACT)


with BuildPart() as body_2_1:
    add(body_2.part)

    # Cut-Extrude1: cut by cut_extrude1_tool
    add(cut_extrude1_tool.part, mode=Mode.SUBTRACT)


solid = Compound([body_3.part, body_4.part, part_1.part, body_2_1.part])
